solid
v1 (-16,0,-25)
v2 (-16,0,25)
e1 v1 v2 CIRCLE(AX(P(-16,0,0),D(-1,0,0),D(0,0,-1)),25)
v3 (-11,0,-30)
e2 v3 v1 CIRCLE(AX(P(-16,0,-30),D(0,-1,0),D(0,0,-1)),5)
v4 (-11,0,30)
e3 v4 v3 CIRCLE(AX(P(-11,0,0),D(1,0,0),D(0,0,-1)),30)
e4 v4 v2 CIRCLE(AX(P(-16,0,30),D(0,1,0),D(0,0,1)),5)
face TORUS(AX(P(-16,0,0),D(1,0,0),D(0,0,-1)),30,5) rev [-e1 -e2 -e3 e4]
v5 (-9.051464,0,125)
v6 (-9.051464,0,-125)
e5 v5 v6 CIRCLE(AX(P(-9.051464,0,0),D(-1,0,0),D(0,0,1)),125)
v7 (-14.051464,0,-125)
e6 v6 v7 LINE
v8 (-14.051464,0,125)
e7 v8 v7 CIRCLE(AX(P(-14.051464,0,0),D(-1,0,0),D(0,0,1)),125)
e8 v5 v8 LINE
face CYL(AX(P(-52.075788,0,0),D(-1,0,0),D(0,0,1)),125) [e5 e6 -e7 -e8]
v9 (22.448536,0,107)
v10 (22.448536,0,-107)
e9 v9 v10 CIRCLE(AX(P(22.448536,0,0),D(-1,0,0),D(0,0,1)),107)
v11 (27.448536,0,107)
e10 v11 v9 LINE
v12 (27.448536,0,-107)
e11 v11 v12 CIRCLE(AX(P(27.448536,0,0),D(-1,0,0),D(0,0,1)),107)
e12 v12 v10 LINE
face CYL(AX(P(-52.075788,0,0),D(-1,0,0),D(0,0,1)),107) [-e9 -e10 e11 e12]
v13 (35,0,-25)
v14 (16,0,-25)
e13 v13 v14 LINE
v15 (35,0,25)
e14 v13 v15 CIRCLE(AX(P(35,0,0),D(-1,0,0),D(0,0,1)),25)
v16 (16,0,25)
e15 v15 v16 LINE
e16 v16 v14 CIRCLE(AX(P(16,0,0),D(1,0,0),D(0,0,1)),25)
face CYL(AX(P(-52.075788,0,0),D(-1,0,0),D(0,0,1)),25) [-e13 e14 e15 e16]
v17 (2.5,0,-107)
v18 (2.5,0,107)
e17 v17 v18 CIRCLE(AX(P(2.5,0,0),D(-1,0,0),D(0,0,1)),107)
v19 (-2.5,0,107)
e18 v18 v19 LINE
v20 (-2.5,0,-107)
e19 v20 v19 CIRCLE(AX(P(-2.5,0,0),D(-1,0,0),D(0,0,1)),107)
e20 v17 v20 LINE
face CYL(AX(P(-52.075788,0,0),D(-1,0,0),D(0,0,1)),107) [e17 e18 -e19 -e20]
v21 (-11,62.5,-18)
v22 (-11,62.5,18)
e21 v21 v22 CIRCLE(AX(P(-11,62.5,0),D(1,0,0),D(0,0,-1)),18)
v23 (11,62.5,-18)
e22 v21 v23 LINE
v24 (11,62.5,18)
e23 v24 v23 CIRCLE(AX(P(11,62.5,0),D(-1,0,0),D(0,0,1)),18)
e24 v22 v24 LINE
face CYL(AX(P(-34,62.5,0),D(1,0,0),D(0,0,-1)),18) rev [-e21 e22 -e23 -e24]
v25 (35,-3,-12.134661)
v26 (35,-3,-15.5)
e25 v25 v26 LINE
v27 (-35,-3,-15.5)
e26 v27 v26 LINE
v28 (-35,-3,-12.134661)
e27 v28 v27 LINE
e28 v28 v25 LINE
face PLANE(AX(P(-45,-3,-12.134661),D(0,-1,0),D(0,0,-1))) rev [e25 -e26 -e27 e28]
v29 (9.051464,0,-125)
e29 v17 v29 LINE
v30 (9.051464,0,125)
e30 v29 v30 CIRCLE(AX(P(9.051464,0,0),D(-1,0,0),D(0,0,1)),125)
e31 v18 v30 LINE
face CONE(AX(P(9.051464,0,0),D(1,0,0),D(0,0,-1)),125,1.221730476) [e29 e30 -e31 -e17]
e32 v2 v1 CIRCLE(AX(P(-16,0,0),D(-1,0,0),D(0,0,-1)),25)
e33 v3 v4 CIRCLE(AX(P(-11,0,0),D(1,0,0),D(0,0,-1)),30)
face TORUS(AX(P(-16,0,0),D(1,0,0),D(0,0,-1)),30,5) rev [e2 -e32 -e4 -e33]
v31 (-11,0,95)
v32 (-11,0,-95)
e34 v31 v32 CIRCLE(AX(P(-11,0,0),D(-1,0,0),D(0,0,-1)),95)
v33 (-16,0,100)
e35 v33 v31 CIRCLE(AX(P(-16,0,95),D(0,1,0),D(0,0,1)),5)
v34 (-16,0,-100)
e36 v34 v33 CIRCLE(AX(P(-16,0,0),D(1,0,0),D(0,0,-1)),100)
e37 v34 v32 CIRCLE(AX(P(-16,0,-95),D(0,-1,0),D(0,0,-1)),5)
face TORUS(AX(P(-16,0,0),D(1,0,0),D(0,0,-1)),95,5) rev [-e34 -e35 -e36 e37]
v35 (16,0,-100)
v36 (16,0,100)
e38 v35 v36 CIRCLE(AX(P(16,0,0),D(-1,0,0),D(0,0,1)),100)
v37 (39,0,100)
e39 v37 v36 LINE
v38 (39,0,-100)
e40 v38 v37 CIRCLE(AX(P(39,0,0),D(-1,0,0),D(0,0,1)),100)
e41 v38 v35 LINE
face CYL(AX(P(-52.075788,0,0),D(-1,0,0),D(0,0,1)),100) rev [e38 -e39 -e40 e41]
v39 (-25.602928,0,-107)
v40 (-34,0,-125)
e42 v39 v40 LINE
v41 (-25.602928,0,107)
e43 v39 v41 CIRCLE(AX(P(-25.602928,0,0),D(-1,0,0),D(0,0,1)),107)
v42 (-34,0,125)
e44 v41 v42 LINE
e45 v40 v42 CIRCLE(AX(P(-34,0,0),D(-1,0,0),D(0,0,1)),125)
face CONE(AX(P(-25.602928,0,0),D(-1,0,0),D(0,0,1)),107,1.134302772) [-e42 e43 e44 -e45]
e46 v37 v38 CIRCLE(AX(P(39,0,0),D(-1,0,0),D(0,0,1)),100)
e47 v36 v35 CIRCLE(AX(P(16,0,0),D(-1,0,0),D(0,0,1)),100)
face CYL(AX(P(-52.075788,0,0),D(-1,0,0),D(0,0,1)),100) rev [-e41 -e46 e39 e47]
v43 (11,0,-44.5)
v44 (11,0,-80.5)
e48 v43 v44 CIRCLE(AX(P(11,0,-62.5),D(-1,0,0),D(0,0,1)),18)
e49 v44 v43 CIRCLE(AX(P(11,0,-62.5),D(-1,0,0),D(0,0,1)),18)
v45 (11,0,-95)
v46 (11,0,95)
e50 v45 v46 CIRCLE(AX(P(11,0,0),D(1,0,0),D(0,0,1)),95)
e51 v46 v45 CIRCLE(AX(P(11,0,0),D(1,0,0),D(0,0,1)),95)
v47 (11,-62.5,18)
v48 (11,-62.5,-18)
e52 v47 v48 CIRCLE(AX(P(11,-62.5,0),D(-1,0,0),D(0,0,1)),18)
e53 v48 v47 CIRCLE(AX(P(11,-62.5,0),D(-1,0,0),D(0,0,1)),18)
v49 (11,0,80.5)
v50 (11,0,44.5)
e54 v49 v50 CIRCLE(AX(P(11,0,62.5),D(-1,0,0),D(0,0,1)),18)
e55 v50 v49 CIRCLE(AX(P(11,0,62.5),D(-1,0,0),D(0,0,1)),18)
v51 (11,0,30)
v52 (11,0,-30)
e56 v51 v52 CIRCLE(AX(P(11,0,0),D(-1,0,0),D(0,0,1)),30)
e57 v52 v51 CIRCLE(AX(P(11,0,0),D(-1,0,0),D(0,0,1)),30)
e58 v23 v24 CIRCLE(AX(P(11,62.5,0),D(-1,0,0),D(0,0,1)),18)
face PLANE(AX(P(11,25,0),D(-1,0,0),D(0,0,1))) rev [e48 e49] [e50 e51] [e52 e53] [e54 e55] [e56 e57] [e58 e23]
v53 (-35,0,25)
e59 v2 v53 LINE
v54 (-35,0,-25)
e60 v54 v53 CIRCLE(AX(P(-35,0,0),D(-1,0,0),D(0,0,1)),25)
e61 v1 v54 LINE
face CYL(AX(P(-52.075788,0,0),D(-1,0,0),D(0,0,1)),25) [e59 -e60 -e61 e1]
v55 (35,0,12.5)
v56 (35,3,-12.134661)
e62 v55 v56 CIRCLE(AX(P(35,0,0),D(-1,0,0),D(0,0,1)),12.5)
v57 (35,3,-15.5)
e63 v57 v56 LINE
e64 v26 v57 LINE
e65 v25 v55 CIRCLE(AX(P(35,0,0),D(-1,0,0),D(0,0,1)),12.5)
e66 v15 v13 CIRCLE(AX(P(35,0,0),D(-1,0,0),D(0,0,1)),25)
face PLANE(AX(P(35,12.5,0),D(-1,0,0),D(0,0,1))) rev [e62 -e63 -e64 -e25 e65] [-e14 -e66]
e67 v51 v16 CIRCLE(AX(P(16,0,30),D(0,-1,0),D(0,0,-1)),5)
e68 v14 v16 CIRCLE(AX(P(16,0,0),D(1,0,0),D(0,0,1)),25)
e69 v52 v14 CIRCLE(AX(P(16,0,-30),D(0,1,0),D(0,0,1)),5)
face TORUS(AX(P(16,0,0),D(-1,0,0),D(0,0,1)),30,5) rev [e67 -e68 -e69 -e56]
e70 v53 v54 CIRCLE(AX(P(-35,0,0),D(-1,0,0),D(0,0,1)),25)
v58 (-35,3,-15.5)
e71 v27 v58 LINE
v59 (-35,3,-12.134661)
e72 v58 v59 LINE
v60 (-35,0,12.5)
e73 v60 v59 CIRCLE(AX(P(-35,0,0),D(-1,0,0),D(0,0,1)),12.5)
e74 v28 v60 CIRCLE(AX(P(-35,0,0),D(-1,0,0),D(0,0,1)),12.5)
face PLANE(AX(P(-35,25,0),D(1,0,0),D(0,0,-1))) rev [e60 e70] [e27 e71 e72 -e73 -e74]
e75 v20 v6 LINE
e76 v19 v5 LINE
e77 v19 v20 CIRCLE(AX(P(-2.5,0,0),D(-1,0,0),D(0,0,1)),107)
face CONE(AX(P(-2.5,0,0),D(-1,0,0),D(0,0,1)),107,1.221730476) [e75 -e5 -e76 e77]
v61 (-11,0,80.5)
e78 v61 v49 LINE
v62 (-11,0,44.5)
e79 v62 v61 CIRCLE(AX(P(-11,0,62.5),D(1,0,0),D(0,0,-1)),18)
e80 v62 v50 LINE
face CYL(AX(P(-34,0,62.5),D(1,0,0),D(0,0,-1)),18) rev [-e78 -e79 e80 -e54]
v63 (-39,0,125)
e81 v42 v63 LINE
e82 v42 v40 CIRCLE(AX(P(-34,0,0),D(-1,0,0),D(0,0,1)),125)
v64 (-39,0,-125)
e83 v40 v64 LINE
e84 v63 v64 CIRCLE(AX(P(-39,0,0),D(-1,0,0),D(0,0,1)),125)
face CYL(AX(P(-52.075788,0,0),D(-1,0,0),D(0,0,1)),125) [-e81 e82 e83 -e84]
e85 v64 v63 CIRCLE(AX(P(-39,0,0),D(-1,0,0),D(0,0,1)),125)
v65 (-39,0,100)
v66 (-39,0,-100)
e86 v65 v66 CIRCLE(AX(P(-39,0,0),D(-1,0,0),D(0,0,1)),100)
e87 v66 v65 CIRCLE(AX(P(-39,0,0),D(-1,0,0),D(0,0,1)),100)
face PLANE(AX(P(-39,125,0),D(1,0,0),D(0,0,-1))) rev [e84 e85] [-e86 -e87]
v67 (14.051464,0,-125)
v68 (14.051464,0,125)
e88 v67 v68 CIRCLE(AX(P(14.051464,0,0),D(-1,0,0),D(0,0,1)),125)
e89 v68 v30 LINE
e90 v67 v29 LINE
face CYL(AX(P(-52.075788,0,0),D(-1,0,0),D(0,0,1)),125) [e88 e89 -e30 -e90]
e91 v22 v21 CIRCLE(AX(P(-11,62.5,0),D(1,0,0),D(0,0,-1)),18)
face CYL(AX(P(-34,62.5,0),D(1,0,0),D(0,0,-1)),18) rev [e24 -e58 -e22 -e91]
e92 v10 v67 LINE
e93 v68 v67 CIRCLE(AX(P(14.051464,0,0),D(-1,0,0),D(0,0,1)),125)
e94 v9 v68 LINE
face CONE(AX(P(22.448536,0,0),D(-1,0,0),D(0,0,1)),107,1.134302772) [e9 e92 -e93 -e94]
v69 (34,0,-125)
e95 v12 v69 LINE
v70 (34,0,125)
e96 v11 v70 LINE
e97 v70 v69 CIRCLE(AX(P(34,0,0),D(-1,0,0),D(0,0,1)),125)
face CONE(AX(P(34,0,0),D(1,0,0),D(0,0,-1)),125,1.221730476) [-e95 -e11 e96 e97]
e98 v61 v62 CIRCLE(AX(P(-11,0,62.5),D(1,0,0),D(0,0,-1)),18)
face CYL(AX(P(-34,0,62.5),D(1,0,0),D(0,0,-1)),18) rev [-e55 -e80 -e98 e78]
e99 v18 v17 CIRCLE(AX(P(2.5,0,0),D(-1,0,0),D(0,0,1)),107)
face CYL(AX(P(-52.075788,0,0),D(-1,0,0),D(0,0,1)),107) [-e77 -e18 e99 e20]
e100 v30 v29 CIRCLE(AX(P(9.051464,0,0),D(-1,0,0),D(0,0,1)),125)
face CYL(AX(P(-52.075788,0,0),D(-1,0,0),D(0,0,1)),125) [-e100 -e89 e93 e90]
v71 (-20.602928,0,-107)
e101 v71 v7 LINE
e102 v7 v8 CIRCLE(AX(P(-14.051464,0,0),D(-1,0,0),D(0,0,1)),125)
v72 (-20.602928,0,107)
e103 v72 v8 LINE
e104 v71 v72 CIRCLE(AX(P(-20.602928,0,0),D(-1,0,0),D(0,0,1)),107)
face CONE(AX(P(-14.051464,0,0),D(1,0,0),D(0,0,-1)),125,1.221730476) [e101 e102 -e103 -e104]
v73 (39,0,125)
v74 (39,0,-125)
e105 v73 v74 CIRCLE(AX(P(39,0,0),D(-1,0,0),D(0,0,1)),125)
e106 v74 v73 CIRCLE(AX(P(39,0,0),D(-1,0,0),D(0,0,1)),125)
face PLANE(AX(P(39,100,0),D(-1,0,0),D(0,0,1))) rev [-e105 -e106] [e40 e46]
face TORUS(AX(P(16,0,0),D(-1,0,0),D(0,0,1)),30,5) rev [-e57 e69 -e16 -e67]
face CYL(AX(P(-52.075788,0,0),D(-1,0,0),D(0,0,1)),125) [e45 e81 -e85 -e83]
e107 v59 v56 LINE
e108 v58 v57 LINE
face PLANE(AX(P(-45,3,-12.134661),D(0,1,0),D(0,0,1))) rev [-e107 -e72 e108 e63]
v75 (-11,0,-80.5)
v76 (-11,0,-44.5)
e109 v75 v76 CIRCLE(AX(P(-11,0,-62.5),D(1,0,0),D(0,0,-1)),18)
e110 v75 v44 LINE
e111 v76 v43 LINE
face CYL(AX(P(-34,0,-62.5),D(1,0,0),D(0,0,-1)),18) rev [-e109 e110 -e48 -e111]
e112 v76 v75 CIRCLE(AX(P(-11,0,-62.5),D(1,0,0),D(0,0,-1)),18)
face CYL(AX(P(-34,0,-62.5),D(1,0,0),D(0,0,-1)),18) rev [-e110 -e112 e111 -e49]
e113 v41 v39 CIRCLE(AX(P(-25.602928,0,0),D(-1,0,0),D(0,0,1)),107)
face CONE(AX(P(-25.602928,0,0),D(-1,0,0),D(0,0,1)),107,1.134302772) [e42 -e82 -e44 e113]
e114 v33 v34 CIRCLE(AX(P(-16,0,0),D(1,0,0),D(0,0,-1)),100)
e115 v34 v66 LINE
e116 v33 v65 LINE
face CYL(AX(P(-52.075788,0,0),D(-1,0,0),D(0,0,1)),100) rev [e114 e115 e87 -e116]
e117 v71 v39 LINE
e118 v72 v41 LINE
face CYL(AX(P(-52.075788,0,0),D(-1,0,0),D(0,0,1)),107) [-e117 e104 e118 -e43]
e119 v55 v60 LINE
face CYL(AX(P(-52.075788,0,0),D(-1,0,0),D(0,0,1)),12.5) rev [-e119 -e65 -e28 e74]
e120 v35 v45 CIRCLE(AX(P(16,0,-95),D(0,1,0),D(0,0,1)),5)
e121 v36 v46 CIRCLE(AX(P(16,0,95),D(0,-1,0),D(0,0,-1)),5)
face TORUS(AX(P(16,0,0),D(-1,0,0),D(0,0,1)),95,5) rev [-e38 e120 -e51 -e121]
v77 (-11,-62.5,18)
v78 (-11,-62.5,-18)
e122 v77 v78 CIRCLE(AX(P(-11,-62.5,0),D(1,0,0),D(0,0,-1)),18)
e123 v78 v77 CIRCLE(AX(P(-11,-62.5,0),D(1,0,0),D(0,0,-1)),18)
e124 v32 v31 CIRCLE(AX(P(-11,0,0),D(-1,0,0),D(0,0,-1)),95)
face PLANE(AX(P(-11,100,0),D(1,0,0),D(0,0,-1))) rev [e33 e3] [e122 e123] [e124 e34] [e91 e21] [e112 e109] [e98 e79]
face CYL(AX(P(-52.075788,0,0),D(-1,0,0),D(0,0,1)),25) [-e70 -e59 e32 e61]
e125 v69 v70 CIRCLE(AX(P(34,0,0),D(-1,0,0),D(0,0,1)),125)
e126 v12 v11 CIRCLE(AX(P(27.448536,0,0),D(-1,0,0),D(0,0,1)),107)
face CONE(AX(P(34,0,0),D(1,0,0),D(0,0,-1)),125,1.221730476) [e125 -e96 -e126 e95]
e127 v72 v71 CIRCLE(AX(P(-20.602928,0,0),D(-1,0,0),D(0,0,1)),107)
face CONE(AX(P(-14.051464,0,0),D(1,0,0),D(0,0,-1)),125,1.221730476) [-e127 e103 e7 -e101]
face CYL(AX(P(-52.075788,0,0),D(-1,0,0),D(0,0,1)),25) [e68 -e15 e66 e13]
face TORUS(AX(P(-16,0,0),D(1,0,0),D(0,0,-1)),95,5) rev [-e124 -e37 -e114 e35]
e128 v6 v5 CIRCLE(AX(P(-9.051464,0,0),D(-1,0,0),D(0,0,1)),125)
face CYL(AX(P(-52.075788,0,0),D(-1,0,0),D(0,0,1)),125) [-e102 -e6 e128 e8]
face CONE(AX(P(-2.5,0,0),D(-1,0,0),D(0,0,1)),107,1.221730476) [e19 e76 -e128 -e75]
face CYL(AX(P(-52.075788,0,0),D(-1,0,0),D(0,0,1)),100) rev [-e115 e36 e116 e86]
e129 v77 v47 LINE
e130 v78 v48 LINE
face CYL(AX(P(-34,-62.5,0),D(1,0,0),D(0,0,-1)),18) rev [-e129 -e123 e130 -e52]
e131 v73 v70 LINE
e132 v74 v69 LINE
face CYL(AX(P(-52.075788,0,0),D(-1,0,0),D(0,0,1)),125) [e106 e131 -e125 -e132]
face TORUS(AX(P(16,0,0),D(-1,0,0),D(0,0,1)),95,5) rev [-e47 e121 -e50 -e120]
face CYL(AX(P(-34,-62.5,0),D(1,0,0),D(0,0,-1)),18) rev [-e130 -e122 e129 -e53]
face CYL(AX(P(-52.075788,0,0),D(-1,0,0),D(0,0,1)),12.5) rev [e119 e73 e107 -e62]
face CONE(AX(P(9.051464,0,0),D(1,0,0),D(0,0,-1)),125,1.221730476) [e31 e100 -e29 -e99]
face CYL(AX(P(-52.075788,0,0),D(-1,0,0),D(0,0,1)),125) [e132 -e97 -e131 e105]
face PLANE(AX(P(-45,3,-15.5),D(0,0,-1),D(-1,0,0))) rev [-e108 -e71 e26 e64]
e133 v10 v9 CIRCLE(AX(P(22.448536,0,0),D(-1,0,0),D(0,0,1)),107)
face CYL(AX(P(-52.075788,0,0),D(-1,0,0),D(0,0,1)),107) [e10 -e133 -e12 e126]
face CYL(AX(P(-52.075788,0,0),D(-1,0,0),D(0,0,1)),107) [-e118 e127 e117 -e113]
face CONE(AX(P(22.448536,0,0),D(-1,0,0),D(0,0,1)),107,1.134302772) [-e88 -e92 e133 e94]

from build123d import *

# Parameters (mm, degrees)
EDGE_FILLET_R5_A_R           = 5
EDGE_FILLET_R5_B_R           = 5
EDGE_FILLET_R5_C_R           = 5
KEYWAY_6X6_DEPTH             = 80
LIGHTENING_HOLES_SKETCH_R    = 18
LIGHTENING_HOLES_4X_36_DEPTH = 45


with BuildPart() as part:
    # Pulley Profile Sketch → Pulley Body Revolve (revolve)
    with BuildSketch(Plane.XY, mode=Mode.PRIVATE) as pulley_body_revolve_sk:
        Polygon((-35, 12.5), (35, 12.5), (35, 25), (11, 25), (11, 100), (39, 100), (39, 125), (34, 125), (27.448535783, 107), (22.448535783, 107), (14.051464217, 125), (9.051464217, 125), (2.5, 107), (-2.5, 107), (-9.051464217, 125), (-14.051464217, 125), (-20.602928434, 107), (-25.602928434, 107), (-34, 125), (-39, 125), (-39, 100), (-11, 100), (-11, 25), (-35, 25), align=None)
    revolve(pulley_body_revolve_sk.sketch.rotate(Axis((-52.075788227, 0, 0), (1, 0, 0)), 90), axis=Axis((-52.075788227, 0, 0), (1, 0, 0)))

    # Edge Fillet R5 A
    edge_fillet_r5_a_edges = [part.edges().sort_by_distance(p)[0] for p in [
        (11, 0, -100),
    ]]
    fillet(edge_fillet_r5_a_edges, radius=EDGE_FILLET_R5_A_R)

    # Edge Fillet R5 B
    edge_fillet_r5_b_edges = [part.edges().sort_by_distance(p)[0] for p in [
        (11, 0, -25),
    ]]
    fillet(edge_fillet_r5_b_edges, radius=EDGE_FILLET_R5_B_R)

    # Edge Fillet R5 C
    edge_fillet_r5_c_edges = [part.edges().sort_by_distance(p)[0] for p in [
        (-11, 0, -25),
        (-11, 0, -100),
    ]]
    fillet(edge_fillet_r5_c_edges, radius=EDGE_FILLET_R5_C_R)

    # Keyway Sketch → Keyway 6x6 (cut)
    with BuildSketch(Plane(origin=(35, 0, 0), x_dir=(0, 0, -1), z_dir=(1, 0, 0))):
        with BuildLine():
            Line((12.1346611, 3), (15.5, 3))
            Line((15.5, 3), (15.5, -3))
            Line((15.5, -3), (12.1346611, -3))
            ThreePointArc((12.1346611, -3), (12.5, 0), (12.1346611, 3))
        make_face()
    extrude(amount=-KEYWAY_6X6_DEPTH, mode=Mode.SUBTRACT)

    # Lightening Holes Sketch → Lightening Holes 4xØ36 (cut, symmetric)
    with BuildSketch(Plane(origin=(11, 0, 0), x_dir=(0, 0, -1), z_dir=(1, 0, 0))):
        with Locations((0, 62.5)):
            Circle(LIGHTENING_HOLES_SKETCH_R)
        with Locations((62.5, 0)):
            Circle(LIGHTENING_HOLES_SKETCH_R)
        with Locations((0, -62.5)):
            Circle(LIGHTENING_HOLES_SKETCH_R)
        with Locations((-62.5, 0)):
            Circle(LIGHTENING_HOLES_SKETCH_R)
    extrude(amount=LIGHTENING_HOLES_4X_36_DEPTH, both=True, mode=Mode.SUBTRACT)


solid = part.part
